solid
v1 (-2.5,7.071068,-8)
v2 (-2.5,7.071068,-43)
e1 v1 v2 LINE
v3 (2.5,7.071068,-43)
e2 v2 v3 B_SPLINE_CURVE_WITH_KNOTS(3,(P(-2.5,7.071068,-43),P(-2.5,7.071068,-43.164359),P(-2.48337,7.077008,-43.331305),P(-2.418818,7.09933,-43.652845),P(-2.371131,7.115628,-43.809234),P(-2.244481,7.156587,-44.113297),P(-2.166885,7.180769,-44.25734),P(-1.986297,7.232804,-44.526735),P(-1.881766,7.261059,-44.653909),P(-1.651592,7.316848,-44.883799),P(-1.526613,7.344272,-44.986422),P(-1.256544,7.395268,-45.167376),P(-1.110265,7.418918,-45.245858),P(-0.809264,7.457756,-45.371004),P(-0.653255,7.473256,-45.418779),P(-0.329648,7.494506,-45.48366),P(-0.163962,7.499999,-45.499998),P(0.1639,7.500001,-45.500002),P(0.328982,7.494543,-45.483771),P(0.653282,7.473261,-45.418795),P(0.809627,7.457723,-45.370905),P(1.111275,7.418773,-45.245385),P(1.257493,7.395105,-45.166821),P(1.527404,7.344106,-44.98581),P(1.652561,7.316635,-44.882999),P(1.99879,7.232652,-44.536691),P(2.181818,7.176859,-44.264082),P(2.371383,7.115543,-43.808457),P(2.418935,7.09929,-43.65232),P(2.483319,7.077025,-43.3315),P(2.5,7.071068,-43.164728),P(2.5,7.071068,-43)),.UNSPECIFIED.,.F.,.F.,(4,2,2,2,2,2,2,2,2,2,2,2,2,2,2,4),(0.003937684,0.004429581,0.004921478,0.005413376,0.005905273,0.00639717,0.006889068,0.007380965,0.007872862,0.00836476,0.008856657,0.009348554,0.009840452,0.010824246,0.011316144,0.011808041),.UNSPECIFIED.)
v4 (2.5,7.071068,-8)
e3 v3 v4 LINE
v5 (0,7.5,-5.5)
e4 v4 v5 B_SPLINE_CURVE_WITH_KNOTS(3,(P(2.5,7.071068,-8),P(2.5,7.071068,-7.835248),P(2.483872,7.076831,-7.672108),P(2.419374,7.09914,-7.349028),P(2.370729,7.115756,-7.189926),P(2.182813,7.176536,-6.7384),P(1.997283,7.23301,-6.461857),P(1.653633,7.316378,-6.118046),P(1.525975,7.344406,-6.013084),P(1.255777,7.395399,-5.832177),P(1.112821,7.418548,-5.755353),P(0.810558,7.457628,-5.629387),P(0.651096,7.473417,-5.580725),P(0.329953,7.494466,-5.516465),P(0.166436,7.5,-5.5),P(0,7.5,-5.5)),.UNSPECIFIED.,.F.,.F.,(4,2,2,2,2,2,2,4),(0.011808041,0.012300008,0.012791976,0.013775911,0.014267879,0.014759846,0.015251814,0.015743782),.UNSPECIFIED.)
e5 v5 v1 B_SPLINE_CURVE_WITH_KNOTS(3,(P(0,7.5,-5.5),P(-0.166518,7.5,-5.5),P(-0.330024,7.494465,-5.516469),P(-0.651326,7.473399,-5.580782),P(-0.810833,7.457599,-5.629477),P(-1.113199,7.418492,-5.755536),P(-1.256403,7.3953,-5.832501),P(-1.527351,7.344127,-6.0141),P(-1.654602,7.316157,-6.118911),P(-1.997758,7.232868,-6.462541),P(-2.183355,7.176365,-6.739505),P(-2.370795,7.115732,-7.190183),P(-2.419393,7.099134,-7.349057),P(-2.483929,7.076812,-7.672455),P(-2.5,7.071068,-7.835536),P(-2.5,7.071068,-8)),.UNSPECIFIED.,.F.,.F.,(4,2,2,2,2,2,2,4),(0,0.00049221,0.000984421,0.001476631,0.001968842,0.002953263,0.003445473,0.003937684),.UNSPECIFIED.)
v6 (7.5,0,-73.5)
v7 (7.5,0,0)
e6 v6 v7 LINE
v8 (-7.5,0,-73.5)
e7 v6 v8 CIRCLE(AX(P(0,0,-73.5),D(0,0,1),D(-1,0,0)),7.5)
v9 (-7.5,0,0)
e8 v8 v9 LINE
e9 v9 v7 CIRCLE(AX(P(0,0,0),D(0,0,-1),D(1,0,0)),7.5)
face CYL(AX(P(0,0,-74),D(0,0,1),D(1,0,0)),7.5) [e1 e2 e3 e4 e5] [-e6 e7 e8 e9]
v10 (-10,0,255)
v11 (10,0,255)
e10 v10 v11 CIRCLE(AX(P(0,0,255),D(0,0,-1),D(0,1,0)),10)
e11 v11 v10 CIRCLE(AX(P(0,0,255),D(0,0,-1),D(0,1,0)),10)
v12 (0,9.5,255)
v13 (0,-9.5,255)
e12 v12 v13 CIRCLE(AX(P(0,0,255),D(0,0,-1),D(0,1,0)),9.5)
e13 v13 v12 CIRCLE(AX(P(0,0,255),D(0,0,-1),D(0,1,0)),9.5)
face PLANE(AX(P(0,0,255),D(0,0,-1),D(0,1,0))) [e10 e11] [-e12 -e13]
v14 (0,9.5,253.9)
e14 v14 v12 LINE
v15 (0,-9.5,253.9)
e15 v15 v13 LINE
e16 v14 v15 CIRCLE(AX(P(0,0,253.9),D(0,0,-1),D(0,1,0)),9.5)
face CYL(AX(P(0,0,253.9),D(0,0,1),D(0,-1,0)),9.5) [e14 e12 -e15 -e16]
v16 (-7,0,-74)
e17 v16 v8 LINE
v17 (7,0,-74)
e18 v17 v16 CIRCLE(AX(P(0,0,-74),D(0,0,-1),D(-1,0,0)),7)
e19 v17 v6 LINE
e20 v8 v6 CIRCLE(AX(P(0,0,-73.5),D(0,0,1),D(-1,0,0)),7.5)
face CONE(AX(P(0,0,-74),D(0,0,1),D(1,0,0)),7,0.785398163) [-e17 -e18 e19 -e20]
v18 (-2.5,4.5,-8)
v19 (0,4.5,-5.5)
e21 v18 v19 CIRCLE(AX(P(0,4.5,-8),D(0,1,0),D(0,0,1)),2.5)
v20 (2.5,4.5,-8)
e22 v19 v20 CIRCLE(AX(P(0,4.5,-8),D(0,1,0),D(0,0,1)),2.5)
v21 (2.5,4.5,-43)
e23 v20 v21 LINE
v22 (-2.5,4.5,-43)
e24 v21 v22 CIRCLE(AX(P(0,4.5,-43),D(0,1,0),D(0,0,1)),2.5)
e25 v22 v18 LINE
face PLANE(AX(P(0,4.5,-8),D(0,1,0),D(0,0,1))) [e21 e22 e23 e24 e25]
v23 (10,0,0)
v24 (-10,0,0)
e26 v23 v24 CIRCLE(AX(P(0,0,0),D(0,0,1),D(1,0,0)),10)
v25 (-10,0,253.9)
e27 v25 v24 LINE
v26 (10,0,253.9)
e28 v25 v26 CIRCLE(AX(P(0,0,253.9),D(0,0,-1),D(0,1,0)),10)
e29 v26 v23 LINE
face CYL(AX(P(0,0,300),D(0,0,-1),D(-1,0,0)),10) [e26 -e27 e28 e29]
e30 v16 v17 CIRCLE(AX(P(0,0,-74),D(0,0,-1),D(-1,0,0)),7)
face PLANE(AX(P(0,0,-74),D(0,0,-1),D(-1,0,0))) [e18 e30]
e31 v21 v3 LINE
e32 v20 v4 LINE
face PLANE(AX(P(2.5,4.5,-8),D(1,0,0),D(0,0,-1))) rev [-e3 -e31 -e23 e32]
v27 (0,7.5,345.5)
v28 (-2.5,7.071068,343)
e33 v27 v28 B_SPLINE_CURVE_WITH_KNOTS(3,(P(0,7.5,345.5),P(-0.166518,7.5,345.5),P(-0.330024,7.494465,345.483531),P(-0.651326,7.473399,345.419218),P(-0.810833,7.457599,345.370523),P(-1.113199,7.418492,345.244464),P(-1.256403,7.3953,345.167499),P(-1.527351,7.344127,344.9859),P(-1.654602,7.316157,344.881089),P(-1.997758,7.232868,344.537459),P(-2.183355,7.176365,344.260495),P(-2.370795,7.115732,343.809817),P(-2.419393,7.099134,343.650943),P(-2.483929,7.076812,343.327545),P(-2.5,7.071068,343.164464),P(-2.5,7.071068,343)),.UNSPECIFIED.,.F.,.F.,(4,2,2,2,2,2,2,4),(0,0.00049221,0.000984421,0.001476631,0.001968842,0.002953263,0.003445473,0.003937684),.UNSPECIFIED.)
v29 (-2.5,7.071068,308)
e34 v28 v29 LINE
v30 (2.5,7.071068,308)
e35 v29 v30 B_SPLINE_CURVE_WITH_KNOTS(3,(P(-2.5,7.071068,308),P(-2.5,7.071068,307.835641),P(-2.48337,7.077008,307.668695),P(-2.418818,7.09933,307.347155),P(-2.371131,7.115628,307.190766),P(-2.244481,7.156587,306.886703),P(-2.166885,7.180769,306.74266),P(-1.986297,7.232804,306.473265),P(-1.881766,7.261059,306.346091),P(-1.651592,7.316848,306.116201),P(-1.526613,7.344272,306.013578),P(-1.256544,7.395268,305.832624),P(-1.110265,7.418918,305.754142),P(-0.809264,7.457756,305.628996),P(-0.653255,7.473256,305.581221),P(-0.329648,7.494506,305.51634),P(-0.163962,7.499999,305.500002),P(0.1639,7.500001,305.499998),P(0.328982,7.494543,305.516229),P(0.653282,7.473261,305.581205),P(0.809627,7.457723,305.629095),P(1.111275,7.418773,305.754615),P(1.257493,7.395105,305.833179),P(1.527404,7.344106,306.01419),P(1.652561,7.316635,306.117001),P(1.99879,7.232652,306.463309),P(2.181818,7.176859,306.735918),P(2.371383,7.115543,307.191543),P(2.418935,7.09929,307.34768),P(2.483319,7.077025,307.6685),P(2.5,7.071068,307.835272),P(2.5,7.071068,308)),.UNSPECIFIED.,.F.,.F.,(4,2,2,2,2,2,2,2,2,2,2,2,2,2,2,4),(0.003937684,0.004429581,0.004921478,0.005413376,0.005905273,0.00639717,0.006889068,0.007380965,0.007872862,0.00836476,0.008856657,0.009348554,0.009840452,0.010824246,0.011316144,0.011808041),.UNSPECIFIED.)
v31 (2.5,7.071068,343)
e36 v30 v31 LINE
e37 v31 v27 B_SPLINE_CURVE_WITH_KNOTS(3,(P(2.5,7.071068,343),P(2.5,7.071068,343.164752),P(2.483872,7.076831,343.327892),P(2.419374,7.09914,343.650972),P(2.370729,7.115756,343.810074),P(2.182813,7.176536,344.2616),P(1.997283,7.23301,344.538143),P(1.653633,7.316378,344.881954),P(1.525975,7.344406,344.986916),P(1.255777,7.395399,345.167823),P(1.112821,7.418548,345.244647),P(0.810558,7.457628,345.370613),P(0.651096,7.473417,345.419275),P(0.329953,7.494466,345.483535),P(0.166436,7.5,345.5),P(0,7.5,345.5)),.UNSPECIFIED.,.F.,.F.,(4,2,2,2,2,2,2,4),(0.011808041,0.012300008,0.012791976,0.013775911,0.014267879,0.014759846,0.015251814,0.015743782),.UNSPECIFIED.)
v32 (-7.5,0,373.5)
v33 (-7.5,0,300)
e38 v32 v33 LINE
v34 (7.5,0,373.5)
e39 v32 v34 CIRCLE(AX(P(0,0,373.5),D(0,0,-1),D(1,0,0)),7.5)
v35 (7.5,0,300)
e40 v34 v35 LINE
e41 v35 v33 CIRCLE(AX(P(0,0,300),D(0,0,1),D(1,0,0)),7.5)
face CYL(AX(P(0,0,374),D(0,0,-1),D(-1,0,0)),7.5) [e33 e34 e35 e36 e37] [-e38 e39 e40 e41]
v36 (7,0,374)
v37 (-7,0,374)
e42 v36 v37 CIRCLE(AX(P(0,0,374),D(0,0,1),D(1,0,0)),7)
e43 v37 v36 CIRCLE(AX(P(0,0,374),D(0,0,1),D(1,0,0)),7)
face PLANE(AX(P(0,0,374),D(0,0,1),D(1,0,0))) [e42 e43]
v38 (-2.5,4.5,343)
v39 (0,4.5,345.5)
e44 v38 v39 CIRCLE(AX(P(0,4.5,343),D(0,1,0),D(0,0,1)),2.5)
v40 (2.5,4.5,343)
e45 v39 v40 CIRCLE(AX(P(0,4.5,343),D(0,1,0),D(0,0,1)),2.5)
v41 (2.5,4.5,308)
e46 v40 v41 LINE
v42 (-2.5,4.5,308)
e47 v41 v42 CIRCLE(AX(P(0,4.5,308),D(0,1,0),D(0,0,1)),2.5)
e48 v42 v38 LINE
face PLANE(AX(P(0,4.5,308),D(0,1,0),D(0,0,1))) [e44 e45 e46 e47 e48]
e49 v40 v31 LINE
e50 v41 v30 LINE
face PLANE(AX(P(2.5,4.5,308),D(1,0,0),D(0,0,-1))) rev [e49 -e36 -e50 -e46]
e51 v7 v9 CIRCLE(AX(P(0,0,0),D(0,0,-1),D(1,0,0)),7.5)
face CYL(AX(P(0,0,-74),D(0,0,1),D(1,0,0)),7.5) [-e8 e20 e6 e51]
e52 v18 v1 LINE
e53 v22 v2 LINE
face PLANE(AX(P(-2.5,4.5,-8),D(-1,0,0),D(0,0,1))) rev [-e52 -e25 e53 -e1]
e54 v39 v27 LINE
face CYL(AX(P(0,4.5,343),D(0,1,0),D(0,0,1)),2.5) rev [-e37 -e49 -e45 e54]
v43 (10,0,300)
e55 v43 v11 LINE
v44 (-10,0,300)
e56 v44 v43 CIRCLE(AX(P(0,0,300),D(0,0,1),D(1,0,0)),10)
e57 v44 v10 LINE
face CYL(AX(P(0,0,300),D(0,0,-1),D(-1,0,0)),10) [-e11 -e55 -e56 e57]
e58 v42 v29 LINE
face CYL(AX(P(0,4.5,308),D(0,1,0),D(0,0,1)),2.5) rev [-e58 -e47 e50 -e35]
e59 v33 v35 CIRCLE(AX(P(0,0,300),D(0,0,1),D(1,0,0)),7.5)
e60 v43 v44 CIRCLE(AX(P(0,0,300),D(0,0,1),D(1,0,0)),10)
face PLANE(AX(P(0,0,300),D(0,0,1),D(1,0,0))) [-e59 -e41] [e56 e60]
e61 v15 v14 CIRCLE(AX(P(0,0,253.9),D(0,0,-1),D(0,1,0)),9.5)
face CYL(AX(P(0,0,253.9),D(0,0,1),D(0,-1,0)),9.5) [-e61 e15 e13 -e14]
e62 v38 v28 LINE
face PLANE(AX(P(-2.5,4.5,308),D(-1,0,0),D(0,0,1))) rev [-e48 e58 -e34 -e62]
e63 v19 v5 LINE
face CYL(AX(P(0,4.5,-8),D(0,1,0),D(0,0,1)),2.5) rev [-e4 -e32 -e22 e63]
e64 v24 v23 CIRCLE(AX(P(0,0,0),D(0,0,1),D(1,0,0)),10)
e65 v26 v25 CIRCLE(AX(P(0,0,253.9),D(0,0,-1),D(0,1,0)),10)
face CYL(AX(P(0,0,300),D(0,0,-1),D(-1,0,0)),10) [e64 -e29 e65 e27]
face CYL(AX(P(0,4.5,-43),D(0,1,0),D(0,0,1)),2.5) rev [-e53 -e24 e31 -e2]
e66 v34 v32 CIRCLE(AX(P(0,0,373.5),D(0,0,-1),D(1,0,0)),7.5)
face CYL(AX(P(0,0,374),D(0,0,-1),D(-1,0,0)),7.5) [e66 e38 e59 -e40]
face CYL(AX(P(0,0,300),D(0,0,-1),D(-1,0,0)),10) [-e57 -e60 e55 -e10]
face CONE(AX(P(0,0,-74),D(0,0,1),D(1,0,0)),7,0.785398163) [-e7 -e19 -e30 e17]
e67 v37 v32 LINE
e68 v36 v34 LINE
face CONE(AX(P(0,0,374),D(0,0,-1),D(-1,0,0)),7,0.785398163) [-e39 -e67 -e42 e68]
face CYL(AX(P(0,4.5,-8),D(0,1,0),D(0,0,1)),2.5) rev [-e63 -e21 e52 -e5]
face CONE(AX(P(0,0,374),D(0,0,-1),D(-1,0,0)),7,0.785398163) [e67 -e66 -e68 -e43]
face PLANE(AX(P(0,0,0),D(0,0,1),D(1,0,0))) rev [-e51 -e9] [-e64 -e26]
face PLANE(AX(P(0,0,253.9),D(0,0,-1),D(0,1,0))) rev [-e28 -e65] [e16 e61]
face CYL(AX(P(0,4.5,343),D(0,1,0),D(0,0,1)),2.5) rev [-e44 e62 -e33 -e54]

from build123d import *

# Parameters (mm, degrees)
SKETCH_1_R          = 10
EXTRUDE_1_DEPTH     = 300
SKETCH_2_R          = 6
EXTRUDE_2_DEPTH     = 74
EXTRUDE_START       = 74
SKETCH_3_R          = 6
EXTRUDE_3_DEPTH     = 74
SKETCH_4_R          = 7.5
EXTRUDE_4_DEPTH     = 74
SKETCH_5_R          = 7.5
EXTRUDE_5_DEPTH     = 74
CUT_EXTRUDE_1_DEPTH = 3
CHAMFER_1_SIZE      = 0.5
SKETCH_8_R          = 12.5
SKETCH_8_R_2        = 9.5
CUT_EXTRUDE_2_DEPTH = 1.1


with BuildPart() as part:
    # 草图1 → 凸台-拉伸1 (new body)
    with BuildSketch(Plane.XY):
        with Locations(Location((0, 0, 0), (0, 0, 90))):
            Circle(SKETCH_1_R)
    extrude(amount=EXTRUDE_1_DEPTH)

    # 草图2 → 凸台-拉伸2 (add)
    with BuildSketch(Plane(origin=(0, 0, 0), x_dir=(-1, 0, 0), z_dir=(0, 0, -1))):
        Circle(SKETCH_2_R)
    extrude(amount=EXTRUDE_2_DEPTH)

    # 草图3 → 凸台-拉伸3 (add)
    with BuildSketch(Plane.XY.offset(300).offset(EXTRUDE_START)):
        Circle(SKETCH_3_R)
    extrude(amount=-EXTRUDE_3_DEPTH)

    # 草图4 → 凸台-拉伸4 (add)
    with BuildSketch(Plane.XY.offset(300)):
        Circle(SKETCH_4_R)
    extrude(amount=EXTRUDE_4_DEPTH)

    # 草图5 → 凸台-拉伸5 (add)
    with BuildSketch(Plane(origin=(0, 0, 0), x_dir=(-1, 0, 0), z_dir=(0, 0, -1)).offset(EXTRUDE_START)):
        with Locations(Location((0, 0, 0), (0, 0, 180))):
            Circle(SKETCH_5_R)
    extrude(amount=-EXTRUDE_5_DEPTH)

    # 草图7 → 切除-拉伸1 (cut)
    with BuildSketch(Plane(origin=(0, 7.5, 0), x_dir=(1, 0, 0), z_dir=(0, 1, 0))):
        with BuildLine():
            Line((-2.5, 8), (-2.5, 43))
            ThreePointArc((-2.5, 43), (0, 45.5), (2.5, 43))
            Line((2.5, 43), (2.5, 8))
            ThreePointArc((2.5, 8), (0, 5.5), (-2.5, 8))
        make_face()
        with BuildLine():
            Line((2.5, -308), (2.5, -343))
            ThreePointArc((2.5, -343), (0, -345.5), (-2.5, -343))
            Line((-2.5, -343), (-2.5, -308))
            ThreePointArc((-2.5, -308), (0, -305.5), (2.5, -308))
        make_face()
    extrude(amount=-CUT_EXTRUDE_1_DEPTH, mode=Mode.SUBTRACT)

    # 倒角1
    chamfer_1_edges = [part.edges().sort_by_distance(p)[0] for p in [
        (-7.5, 0, 374),
        (-7.5, 0, -74),
    ]]
    chamfer(chamfer_1_edges, length=CHAMFER_1_SIZE)

    # 草图8 → 切除-拉伸2 (cut)
    with BuildSketch(Plane(origin=(0, 0, 255), x_dir=(-1, 0, 0), z_dir=(0, 0, -1))):
        Circle(SKETCH_8_R)
        with Locations(Location((0, 0, 0), (0, 0, 90))):
            Circle(SKETCH_8_R_2, mode=Mode.SUBTRACT)
    extrude(amount=CUT_EXTRUDE_2_DEPTH, mode=Mode.SUBTRACT)


solid = part.part
